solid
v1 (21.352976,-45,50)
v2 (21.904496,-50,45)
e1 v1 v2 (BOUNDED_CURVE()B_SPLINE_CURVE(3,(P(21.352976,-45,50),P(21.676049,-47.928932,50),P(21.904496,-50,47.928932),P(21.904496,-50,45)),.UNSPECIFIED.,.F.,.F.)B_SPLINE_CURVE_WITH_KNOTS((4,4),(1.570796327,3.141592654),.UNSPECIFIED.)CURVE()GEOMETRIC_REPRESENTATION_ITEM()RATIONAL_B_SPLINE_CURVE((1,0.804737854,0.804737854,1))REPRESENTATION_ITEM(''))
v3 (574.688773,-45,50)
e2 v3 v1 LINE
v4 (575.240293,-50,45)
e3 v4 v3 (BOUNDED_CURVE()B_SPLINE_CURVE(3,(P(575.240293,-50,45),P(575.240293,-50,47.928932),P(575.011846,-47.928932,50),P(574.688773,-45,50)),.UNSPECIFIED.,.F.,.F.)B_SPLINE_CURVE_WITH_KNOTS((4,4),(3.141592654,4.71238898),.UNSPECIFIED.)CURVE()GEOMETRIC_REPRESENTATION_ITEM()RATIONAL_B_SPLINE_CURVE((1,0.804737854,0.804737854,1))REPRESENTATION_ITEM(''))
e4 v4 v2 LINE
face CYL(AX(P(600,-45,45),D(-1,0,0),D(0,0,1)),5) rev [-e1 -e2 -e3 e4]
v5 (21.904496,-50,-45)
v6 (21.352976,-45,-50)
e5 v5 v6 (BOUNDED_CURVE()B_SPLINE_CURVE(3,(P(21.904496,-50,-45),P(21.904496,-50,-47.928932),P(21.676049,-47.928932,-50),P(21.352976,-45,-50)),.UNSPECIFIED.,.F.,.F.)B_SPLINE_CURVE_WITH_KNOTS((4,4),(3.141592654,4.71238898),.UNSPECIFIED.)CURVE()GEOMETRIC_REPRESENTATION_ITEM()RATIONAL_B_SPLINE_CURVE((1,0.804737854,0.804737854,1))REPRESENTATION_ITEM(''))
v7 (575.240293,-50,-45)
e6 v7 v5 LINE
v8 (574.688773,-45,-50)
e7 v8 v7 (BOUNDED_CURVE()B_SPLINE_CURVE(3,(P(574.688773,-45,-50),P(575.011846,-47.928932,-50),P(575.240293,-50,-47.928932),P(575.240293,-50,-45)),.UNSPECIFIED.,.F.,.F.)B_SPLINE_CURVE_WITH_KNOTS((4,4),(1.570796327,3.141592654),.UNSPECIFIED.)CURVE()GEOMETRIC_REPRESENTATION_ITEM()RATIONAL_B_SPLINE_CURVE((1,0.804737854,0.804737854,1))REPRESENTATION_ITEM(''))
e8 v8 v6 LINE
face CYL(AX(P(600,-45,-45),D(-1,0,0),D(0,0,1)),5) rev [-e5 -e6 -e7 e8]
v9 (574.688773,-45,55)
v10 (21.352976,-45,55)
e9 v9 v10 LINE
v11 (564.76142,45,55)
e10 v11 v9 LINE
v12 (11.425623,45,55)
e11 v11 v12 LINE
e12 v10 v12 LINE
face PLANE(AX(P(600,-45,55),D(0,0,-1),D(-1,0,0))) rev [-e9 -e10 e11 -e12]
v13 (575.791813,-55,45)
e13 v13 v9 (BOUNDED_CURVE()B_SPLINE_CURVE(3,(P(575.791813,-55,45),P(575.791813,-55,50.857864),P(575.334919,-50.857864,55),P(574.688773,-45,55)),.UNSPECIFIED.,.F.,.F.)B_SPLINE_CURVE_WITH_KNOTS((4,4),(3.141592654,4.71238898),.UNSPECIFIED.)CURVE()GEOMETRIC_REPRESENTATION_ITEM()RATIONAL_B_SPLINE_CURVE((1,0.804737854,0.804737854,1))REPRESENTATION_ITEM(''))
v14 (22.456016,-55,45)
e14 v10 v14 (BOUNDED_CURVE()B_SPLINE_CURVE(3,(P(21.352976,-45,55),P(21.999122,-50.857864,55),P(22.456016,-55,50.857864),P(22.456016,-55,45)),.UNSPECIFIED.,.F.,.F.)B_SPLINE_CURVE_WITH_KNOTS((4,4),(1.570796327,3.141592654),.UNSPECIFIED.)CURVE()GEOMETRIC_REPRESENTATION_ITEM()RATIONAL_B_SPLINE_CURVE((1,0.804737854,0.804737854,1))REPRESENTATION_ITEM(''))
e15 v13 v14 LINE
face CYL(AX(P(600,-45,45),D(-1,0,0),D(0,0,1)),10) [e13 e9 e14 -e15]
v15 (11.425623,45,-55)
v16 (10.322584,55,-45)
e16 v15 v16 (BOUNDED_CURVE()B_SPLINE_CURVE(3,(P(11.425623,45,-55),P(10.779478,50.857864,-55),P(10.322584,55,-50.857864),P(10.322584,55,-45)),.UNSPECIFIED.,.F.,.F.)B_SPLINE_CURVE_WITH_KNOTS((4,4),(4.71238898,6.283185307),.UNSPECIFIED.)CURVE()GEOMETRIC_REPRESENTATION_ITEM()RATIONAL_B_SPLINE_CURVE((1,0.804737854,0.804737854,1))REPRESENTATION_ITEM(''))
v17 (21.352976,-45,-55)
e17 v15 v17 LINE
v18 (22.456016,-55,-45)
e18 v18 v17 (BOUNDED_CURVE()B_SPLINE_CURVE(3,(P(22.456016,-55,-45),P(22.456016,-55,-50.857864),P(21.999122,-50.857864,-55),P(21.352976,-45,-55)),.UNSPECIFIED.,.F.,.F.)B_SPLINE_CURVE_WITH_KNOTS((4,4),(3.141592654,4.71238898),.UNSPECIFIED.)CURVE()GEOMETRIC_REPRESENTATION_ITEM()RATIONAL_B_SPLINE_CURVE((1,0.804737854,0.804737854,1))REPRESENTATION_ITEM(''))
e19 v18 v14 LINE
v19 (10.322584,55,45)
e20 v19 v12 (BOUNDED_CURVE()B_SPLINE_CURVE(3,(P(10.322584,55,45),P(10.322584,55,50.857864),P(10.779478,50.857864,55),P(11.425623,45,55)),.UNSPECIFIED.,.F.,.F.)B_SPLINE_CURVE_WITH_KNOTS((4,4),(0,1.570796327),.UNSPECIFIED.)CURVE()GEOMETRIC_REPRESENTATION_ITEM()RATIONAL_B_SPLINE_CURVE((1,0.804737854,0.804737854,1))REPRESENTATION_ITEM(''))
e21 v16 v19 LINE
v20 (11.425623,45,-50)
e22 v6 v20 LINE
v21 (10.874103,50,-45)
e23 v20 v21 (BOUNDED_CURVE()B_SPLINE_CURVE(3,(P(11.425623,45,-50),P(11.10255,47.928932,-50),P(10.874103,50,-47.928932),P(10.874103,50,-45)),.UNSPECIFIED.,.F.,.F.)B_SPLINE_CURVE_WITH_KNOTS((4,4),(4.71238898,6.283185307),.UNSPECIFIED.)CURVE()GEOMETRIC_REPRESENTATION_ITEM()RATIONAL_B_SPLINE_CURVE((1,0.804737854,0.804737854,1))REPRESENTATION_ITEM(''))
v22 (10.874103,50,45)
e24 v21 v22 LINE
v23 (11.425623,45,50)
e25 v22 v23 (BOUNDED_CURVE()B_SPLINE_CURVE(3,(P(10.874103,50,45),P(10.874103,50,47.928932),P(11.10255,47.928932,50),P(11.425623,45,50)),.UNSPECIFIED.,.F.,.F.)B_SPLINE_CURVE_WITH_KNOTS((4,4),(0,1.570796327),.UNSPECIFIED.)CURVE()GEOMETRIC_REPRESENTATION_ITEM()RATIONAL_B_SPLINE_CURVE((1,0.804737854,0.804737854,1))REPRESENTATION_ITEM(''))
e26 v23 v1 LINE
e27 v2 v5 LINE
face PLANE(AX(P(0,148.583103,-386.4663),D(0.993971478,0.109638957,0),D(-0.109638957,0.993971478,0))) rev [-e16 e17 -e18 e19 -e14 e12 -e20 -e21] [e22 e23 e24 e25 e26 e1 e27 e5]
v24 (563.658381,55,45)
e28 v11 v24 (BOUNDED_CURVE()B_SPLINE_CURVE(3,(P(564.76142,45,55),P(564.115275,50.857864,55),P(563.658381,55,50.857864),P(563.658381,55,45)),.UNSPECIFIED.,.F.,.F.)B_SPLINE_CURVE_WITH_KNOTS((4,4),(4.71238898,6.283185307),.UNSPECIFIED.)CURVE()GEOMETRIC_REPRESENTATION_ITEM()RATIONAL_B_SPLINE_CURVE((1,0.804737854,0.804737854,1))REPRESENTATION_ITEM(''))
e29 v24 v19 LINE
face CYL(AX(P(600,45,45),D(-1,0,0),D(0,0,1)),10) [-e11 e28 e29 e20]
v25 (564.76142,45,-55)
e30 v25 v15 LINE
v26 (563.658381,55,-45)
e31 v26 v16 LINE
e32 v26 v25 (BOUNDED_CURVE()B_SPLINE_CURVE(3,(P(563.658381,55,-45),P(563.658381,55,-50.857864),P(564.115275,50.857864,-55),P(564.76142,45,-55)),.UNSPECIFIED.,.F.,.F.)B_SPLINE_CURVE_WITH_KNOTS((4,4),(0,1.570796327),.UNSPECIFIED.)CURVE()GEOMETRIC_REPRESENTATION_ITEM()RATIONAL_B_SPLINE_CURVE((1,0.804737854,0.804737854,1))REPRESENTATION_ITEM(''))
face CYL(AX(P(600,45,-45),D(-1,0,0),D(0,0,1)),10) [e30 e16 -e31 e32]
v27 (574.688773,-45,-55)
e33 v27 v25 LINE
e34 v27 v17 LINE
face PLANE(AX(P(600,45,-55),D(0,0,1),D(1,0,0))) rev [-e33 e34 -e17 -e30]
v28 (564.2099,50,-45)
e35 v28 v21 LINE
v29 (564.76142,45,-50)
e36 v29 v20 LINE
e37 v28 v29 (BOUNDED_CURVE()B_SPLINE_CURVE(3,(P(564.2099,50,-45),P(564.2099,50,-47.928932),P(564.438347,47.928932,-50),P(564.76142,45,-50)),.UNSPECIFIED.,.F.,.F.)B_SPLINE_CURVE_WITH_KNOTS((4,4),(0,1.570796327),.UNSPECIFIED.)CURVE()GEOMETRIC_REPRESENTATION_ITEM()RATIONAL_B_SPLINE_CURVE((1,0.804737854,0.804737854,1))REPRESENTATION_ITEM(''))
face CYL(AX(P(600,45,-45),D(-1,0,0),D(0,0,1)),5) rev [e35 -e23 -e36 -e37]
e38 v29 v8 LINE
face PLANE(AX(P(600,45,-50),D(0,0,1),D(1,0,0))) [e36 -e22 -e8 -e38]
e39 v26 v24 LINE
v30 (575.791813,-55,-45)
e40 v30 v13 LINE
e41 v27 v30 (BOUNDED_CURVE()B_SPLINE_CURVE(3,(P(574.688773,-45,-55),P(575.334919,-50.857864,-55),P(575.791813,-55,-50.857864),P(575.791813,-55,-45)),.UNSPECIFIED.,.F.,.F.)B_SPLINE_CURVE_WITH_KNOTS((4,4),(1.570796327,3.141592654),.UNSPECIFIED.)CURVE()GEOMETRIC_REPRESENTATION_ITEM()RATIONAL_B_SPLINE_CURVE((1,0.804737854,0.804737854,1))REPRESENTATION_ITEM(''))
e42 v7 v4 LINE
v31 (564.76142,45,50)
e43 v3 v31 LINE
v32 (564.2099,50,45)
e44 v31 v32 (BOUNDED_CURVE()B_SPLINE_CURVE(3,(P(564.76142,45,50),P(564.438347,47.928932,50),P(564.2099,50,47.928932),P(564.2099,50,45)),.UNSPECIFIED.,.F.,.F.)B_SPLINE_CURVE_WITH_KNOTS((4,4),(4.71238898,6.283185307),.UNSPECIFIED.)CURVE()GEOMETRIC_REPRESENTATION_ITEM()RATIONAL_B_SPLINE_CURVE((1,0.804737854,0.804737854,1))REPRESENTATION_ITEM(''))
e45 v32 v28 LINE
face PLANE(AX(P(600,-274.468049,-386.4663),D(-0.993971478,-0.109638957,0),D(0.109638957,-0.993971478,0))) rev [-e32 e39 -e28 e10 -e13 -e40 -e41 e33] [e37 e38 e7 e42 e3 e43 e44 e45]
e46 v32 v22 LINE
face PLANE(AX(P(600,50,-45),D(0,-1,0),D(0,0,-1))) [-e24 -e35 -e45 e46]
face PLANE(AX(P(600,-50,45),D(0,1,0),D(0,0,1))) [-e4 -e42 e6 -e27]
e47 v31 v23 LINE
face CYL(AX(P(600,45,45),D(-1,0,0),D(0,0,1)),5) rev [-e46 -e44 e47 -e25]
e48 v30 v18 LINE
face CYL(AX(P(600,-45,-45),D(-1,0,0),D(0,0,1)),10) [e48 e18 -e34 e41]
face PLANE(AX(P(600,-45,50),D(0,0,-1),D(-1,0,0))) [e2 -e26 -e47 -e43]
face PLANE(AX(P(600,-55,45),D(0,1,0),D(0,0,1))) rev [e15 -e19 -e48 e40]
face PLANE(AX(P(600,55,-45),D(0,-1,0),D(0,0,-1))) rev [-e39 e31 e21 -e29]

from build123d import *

# Parameters (mm, degrees)
F_110_X_110_X_5_1_DEPTH = 600
CUT_EXTRUDE_1_REACH     = 614.474


with BuildPart() as part:
    # Sketch1 → 方形管 110 X 110 X 5(1) (new body)
    with BuildSketch(Plane(origin=(0, 0, 0), x_dir=(0, 0, -1), z_dir=(1, 0, 0))):
        with BuildLine():
            Line((-45, -55), (45, -55))
            ThreePointArc((45, -55), (52.071067812, -52.071067812), (55, -45))
            Line((55, -45), (55, 45))
            ThreePointArc((55, 45), (52.071067812, 52.071067812), (45, 55))
            Line((45, 55), (-45, 55))
            ThreePointArc((-45, 55), (-52.071067812, 52.071067812), (-55, 45))
            Line((-55, 45), (-55, -45))
            ThreePointArc((-55, -45), (-52.071067812, -52.071067812), (-45, -55))
        make_face()
        with BuildLine():
            Line((-45, -50), (45, -50))
            ThreePointArc((45, -50), (48.535533906, -48.535533906), (50, -45))
            Line((50, -45), (50, 45))
            ThreePointArc((50, 45), (48.535533906, 48.535533906), (45, 50))
            Line((45, 50), (-45, 50))
            ThreePointArc((-45, 50), (-48.535533906, 48.535533906), (-50, 45))
            Line((-50, 45), (-50, -45))
            ThreePointArc((-50, -45), (-48.535533906, -48.535533906), (-45, -50))
        make_face(mode=Mode.SUBTRACT)
    extrude(amount=F_110_X_110_X_5_1_DEPTH)

    # 切除-拉伸1: up to this face of the body (flat: up to its plane)
    cut_extrude_1_end = Plane(part.part.faces().sort_by_distance((300, 0, -55))[0])
    # 草图2 → 切除-拉伸1 (cut, up to the picked face)
    with BuildSketch(Plane.XY.offset(55), mode=Mode.PRIVATE) as cut_extrude_1_sk1:
        Polygon((0, 148.583103171), (22.456015583, -55), (0, -55), align=None)
    cut_extrude_1_tool1 = split(extrude(cut_extrude_1_sk1.sketch, amount=-CUT_EXTRUDE_1_REACH, mode=Mode.PRIVATE), bisect_by=cut_extrude_1_end, keep=Keep.BOTH, mode=Mode.PRIVATE)
    # 草图2 → 切除-拉伸1 (cut, up to the picked face)
    with BuildSketch(Plane.XY.offset(55), mode=Mode.PRIVATE) as cut_extrude_1_sk2:
        Polygon((600, -274.46804857), (563.658380693, 55), (600, 55), align=None)
    cut_extrude_1_tool2 = split(extrude(cut_extrude_1_sk2.sketch, amount=-CUT_EXTRUDE_1_REACH, mode=Mode.PRIVATE), bisect_by=cut_extrude_1_end, keep=Keep.BOTH, mode=Mode.PRIVATE)
    add(cut_extrude_1_tool1.solids().sort_by(Axis((7.485339, 12.861034, 55), (0, 0, -1)))[0], mode=Mode.SUBTRACT)
    add(cut_extrude_1_tool2.solids().sort_by(Axis((587.886127, -54.822683, 55), (0, 0, -1)))[0], mode=Mode.SUBTRACT)


solid = part.part
